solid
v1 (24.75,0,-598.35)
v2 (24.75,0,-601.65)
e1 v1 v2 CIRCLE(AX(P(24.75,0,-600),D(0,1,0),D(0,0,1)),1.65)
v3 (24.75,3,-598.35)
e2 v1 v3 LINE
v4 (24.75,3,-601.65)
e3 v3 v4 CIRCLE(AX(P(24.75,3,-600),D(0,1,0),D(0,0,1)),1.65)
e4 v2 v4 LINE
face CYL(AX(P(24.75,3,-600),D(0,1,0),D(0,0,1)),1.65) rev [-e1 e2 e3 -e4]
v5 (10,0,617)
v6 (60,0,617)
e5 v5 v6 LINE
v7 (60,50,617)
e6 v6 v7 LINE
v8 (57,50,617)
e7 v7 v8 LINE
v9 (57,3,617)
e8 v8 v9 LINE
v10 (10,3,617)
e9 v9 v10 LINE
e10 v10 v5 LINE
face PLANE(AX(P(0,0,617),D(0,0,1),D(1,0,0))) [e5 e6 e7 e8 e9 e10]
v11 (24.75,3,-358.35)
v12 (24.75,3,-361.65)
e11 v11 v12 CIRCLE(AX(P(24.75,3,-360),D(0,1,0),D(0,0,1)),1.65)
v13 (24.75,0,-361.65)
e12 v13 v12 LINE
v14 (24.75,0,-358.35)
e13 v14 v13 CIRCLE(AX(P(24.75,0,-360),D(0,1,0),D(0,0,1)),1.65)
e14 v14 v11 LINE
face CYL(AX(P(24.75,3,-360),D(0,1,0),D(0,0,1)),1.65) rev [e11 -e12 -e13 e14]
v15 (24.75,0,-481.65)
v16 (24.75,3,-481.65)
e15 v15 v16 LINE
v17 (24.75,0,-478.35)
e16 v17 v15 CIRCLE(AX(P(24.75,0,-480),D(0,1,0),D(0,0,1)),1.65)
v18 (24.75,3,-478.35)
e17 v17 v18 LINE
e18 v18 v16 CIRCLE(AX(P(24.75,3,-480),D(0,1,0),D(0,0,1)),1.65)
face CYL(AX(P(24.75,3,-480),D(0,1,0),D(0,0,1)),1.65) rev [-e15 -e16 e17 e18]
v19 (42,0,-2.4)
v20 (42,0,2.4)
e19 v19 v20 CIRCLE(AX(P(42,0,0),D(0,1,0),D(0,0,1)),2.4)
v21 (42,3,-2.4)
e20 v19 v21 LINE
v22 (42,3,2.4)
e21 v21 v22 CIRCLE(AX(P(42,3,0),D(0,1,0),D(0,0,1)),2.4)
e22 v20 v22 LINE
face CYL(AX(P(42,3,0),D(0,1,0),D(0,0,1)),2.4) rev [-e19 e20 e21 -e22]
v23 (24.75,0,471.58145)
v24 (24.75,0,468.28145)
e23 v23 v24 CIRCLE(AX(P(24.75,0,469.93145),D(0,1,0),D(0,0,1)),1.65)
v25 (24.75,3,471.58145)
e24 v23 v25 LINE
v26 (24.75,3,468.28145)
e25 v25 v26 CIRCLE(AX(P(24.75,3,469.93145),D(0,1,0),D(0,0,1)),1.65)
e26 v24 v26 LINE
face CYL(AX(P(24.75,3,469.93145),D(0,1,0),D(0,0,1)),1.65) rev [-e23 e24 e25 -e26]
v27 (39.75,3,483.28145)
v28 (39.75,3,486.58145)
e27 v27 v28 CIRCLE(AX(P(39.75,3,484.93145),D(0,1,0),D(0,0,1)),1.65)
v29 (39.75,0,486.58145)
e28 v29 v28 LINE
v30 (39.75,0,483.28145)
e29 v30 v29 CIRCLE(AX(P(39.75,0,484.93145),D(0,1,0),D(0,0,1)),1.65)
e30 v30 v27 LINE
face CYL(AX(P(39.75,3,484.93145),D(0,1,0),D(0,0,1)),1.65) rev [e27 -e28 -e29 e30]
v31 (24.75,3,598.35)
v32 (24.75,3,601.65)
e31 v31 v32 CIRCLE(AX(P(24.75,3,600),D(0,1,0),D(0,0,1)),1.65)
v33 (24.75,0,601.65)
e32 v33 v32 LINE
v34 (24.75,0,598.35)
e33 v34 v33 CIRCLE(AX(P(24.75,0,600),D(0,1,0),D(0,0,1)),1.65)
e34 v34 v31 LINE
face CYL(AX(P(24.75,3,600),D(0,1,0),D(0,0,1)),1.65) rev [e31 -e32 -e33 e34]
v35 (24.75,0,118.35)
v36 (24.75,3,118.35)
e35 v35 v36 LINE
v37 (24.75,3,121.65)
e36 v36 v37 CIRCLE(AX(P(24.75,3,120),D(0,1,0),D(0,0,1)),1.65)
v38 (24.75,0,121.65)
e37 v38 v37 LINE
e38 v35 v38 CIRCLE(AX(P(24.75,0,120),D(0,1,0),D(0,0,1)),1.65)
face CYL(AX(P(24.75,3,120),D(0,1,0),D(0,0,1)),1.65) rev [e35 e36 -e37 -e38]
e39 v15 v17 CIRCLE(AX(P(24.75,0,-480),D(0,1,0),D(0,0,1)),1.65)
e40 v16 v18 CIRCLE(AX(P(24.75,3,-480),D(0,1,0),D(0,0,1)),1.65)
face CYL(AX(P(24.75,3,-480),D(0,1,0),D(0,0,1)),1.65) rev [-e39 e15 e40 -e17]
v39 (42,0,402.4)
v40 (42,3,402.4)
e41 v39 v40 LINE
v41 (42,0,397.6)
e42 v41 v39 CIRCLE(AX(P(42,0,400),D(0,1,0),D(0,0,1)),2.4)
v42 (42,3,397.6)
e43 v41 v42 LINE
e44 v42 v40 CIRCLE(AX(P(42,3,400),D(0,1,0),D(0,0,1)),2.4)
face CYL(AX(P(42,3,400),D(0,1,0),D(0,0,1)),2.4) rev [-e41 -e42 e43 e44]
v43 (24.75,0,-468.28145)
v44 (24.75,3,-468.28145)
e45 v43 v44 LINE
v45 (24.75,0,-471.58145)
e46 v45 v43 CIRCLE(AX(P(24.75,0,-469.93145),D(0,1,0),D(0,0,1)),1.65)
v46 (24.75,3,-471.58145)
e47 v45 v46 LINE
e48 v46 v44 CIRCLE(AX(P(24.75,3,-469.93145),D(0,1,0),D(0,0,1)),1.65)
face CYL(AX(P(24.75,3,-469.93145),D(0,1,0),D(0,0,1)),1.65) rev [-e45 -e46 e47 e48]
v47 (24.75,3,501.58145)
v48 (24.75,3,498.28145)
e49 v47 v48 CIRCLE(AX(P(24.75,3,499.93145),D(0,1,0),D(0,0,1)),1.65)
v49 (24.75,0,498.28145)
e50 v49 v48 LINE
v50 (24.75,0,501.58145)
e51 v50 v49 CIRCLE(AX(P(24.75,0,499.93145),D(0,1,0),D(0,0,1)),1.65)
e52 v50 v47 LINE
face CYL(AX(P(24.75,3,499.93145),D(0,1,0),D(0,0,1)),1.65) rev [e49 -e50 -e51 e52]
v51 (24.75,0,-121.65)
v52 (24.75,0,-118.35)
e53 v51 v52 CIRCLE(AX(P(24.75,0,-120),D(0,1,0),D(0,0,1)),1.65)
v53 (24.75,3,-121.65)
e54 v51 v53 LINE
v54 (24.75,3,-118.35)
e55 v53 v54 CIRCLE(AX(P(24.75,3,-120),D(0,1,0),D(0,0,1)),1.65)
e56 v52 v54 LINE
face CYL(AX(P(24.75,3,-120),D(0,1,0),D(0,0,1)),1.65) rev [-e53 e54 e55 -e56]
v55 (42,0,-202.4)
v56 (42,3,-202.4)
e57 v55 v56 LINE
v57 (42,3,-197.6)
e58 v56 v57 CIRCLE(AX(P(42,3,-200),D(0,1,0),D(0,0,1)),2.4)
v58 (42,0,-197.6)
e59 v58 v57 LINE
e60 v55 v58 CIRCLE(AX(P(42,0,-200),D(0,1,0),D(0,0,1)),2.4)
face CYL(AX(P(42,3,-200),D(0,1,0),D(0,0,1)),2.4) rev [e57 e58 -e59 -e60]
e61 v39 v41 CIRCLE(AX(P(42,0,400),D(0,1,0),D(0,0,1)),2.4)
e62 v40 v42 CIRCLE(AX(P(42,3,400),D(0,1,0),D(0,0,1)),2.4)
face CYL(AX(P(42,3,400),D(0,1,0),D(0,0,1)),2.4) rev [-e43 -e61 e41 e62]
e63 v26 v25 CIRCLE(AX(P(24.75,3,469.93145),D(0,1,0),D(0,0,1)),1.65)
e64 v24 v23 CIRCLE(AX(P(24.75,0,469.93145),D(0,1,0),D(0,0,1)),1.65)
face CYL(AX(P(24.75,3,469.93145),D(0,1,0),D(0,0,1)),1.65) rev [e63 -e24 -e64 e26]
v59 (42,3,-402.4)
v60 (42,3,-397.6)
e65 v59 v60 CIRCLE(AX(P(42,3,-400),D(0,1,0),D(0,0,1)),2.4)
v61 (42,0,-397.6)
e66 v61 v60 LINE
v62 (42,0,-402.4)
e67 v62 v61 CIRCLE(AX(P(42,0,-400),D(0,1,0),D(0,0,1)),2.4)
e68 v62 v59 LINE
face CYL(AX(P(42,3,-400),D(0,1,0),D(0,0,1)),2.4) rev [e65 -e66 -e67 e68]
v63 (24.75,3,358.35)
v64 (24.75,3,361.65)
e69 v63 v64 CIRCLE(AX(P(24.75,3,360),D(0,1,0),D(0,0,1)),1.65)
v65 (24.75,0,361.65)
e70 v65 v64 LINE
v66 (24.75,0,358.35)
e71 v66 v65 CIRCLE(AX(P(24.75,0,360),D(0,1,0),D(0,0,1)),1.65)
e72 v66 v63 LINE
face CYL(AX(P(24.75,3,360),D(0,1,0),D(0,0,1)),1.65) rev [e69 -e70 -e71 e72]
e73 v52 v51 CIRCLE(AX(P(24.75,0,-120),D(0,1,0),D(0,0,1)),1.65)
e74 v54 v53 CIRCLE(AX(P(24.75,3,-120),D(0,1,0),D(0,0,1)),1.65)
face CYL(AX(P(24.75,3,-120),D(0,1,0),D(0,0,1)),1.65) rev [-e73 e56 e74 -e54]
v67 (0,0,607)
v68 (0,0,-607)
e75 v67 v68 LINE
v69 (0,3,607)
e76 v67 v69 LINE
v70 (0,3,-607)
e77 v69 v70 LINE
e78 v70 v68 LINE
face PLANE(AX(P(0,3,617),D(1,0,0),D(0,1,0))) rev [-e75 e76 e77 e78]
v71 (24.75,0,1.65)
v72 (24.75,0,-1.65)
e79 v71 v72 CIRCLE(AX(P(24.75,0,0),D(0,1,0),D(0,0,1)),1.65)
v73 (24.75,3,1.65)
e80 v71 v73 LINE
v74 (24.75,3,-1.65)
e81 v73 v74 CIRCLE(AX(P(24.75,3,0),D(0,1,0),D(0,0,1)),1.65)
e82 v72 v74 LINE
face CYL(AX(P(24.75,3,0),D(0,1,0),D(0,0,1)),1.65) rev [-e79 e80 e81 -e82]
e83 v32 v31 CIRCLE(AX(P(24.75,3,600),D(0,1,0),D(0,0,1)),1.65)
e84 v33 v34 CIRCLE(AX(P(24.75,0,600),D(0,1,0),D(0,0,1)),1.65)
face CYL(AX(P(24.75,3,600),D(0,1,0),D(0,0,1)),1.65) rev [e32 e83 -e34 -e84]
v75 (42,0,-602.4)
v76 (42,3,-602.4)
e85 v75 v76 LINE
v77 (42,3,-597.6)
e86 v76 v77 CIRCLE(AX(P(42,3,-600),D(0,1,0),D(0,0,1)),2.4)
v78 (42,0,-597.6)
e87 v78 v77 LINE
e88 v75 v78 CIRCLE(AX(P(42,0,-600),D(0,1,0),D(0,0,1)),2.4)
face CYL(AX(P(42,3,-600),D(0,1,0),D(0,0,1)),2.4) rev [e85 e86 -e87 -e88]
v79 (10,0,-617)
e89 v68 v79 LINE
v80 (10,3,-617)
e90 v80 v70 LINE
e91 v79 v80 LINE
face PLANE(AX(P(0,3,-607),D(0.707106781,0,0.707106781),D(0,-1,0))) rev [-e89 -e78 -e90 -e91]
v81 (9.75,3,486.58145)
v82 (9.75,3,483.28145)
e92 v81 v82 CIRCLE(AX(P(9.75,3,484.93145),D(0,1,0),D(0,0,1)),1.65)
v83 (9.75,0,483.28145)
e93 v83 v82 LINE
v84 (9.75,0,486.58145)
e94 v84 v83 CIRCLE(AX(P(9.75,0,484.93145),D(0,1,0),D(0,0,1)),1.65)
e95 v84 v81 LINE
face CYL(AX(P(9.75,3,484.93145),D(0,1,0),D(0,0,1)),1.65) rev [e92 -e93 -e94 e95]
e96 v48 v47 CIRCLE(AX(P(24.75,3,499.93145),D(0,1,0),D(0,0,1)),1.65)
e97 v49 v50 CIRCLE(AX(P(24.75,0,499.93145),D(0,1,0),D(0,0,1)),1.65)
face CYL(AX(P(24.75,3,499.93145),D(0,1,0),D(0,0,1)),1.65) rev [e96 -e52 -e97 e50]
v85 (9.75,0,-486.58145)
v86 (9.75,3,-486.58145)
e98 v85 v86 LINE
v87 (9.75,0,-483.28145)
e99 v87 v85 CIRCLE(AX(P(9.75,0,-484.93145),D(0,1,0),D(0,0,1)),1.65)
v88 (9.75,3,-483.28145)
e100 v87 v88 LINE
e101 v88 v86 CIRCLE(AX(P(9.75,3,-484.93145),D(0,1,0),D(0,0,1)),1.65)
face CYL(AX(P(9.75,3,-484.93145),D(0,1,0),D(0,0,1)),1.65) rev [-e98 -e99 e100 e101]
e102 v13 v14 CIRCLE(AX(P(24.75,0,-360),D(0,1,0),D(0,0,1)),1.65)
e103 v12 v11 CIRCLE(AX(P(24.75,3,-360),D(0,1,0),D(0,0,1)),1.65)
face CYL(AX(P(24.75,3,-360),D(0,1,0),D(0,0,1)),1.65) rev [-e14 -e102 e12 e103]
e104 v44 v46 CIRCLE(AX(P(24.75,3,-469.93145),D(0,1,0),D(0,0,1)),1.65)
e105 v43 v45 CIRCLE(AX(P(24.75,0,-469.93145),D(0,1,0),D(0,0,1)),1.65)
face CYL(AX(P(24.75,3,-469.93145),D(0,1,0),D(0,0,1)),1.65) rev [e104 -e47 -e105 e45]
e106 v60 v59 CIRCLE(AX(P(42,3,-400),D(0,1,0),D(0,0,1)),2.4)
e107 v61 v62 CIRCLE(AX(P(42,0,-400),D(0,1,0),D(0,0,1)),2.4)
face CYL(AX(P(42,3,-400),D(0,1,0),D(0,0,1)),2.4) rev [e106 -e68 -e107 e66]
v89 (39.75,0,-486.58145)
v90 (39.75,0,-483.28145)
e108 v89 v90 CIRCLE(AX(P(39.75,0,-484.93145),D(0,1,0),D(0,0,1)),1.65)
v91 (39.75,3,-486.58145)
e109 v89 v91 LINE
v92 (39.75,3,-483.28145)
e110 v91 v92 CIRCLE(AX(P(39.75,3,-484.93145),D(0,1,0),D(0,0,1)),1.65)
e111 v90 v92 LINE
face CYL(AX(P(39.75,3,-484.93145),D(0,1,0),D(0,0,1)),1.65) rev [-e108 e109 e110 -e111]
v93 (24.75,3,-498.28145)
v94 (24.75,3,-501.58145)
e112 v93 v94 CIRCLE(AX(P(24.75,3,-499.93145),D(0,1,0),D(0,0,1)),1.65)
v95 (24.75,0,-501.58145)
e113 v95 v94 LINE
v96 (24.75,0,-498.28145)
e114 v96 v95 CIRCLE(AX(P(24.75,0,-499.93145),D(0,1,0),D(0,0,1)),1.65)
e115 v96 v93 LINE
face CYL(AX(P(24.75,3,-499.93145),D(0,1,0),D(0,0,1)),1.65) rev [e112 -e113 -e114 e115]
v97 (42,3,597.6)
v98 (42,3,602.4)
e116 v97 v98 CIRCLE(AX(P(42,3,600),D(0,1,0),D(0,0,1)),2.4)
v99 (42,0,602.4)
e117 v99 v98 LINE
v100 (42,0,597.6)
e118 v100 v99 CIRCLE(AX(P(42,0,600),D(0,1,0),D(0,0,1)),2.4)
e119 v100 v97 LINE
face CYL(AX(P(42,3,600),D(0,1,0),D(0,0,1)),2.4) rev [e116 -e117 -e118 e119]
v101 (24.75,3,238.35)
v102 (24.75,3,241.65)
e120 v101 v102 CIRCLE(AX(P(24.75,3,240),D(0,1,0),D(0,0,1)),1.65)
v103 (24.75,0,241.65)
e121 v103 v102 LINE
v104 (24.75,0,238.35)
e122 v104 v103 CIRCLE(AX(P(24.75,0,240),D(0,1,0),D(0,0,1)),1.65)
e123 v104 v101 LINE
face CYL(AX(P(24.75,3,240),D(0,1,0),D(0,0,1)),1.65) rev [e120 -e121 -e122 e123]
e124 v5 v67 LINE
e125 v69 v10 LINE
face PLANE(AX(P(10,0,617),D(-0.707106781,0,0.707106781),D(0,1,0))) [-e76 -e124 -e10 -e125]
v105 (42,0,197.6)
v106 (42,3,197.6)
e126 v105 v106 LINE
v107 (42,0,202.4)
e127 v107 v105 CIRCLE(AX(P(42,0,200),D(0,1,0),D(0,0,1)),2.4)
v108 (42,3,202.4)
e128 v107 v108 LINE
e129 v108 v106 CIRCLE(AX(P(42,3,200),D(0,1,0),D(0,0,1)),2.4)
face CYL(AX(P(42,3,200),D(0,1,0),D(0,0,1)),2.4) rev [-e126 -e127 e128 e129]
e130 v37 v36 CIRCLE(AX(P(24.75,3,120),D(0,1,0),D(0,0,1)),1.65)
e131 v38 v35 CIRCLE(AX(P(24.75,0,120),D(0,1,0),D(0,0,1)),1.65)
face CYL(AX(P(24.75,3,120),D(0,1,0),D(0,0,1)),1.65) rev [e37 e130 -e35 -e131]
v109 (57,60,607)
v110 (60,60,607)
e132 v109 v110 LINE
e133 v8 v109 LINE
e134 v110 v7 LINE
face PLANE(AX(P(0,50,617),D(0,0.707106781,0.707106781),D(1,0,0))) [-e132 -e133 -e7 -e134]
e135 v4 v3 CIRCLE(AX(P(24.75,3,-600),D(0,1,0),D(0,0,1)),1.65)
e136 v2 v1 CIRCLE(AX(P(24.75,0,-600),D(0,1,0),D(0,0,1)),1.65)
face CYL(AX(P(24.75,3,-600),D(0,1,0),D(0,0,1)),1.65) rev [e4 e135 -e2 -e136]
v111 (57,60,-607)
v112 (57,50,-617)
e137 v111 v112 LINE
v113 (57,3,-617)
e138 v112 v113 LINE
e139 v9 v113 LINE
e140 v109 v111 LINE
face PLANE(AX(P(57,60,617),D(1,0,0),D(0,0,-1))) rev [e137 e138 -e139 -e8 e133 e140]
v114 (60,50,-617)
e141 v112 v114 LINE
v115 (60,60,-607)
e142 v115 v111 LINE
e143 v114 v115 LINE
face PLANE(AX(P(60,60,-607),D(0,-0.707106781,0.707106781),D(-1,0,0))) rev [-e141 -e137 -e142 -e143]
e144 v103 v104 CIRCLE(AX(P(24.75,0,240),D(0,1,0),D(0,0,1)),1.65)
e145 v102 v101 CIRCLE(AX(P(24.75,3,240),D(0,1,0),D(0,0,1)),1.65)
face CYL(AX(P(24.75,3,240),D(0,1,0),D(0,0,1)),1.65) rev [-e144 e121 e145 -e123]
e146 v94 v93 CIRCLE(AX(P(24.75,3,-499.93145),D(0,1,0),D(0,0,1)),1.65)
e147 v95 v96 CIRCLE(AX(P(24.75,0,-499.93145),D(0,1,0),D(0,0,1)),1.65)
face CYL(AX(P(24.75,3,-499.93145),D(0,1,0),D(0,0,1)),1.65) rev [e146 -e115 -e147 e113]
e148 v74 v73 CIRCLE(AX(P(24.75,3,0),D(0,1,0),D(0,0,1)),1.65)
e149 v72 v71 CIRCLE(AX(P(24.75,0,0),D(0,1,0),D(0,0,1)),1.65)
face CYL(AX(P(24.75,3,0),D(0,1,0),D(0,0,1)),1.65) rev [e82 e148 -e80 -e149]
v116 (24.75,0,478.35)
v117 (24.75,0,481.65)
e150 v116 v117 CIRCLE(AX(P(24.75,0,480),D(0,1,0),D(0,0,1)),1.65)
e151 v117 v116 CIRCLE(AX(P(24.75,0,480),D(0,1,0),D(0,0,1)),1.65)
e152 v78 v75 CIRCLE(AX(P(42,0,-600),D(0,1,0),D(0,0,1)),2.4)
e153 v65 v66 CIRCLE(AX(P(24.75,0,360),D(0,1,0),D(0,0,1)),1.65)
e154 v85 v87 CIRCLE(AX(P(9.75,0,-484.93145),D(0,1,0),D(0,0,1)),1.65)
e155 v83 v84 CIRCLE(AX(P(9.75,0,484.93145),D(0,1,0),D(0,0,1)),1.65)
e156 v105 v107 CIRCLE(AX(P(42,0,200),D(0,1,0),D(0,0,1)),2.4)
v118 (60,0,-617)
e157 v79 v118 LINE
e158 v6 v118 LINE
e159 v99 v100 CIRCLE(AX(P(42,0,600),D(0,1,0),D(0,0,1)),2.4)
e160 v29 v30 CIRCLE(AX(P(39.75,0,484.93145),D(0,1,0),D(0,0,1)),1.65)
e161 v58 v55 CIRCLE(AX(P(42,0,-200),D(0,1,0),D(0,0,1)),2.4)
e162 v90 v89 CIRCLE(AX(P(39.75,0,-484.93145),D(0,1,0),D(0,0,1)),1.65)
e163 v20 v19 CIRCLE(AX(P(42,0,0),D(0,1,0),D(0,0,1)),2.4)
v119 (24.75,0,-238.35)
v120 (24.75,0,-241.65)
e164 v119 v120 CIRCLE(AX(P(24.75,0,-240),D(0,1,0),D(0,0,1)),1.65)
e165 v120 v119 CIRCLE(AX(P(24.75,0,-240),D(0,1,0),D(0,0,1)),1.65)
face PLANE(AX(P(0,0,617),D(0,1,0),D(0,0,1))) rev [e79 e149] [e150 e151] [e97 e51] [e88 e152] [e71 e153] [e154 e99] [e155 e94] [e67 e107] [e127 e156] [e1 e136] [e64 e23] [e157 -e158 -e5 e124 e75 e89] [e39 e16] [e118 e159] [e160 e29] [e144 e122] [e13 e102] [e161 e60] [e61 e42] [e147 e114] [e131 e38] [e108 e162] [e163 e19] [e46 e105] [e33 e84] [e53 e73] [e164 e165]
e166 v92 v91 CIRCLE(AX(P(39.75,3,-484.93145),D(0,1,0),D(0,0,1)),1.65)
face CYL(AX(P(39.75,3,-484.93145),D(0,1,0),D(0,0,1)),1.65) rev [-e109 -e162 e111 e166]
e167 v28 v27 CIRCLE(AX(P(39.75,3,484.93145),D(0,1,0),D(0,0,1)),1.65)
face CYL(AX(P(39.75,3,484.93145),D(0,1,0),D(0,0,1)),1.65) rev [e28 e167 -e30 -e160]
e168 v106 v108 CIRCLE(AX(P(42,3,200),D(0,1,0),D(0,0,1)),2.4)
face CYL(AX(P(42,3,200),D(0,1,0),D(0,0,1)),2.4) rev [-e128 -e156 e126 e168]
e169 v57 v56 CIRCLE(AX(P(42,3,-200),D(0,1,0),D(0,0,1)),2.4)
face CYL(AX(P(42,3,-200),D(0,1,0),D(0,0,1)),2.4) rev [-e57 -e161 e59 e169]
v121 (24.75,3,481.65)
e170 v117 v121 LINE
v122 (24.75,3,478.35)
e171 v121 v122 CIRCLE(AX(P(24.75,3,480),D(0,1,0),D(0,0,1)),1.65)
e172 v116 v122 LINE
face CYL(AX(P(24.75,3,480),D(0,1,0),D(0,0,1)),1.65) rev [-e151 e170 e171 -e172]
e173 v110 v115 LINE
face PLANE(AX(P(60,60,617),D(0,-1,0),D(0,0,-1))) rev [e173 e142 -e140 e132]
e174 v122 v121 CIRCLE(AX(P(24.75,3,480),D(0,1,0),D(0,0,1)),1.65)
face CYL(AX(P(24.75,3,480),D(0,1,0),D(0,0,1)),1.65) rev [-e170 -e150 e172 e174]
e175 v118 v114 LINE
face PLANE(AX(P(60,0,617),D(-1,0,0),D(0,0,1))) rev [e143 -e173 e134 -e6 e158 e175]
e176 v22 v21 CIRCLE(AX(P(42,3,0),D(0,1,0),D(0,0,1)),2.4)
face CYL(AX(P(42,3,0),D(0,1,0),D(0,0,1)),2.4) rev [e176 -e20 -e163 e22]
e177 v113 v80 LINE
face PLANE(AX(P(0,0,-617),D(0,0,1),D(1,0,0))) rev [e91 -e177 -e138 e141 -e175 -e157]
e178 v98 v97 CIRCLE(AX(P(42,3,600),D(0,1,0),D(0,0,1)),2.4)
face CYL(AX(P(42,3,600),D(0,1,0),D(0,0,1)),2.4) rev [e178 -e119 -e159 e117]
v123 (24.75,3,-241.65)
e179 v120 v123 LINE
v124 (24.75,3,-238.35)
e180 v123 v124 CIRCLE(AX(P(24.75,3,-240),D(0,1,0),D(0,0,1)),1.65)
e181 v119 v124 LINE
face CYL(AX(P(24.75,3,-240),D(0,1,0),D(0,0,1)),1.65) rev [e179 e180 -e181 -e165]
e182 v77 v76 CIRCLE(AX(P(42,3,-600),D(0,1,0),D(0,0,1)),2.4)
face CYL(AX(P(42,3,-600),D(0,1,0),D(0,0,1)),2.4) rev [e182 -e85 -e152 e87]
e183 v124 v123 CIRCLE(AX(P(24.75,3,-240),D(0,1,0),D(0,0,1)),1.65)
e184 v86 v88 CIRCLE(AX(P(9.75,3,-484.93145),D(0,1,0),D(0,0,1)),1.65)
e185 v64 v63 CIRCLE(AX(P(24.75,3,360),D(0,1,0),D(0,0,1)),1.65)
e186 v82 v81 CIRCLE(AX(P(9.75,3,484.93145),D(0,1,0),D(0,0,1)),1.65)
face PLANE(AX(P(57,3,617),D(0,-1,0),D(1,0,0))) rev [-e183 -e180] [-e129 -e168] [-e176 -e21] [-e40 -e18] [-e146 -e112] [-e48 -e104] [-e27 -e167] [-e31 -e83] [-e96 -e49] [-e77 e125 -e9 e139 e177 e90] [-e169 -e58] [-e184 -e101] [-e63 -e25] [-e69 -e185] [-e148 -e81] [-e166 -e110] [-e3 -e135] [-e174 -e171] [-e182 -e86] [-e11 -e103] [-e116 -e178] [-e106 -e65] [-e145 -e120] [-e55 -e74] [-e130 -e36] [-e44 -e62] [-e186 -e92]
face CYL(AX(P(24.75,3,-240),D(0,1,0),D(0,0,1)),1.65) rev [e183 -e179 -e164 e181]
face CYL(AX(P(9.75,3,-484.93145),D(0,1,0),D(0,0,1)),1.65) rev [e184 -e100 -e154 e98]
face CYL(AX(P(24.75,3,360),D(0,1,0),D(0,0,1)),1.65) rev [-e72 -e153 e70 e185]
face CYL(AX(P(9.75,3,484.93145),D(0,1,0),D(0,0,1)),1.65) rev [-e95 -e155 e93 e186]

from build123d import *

# Parameters (mm, degrees)
EXTRUDE_1_DEPTH        = 617
HOLE_WIZARD_M4_2_D     = 3.3
HOLE_WIZARD_M4_3_D     = 3.3
HOLE_WIZARD_M4_3_DEPTH = 3
HOLE_WIZARD_M4_1_D     = 4.8
HOLE_WIZARD_M4_4_D     = 3.3
CHAMFER_1_SIZE         = 10


with BuildPart() as part:
    # 草图1 → 凸台-拉伸1 (new, symmetric)
    with BuildSketch(Plane.XY):
        Polygon((0, 0), (60, 0), (60, 60), (57, 60), (57, 3), (0, 3), align=None)
    extrude(amount=EXTRUDE_1_DEPTH, both=True)

    # M4 螺纹孔2 (through all)
    with Locations(Plane(origin=(0, 3, 0), x_dir=(1, 0, 0), z_dir=(0, 1, 0))):
        with Locations((24.75, 499.931449769), (9.75, 484.931449769), (39.75, 484.931449769), (39.75, -484.931449769), (9.75, -484.931449769), (24.75, -499.931449769)):
            Hole(HOLE_WIZARD_M4_2_D / 2)

    # M4 螺纹孔3
    with Locations(Plane(origin=(0, 3, 0), x_dir=(1, 0, 0), z_dir=(0, 1, 0))):
        with Locations((9.75, 484.931449769), (39.75, 484.931449769), (24.75, 469.931449769), (24.75, 499.931449769), (24.75, -499.931449769), (24.75, -469.931449769), (39.75, -484.931449769), (9.75, -484.931449769)):
            Hole(HOLE_WIZARD_M4_3_D / 2, depth=HOLE_WIZARD_M4_3_DEPTH)

    # M4 间隙孔1 (through all)
    with Locations(Plane(origin=(0, 3, 0), x_dir=(1, 0, 0), z_dir=(0, 1, 0))):
        with Locations((42, 0), (42, 200), (42, 400), (42, 600), (42, -600), (42, -400), (42, -200)):
            Hole(HOLE_WIZARD_M4_1_D / 2)

    # M4 螺纹孔4 (through all)
    with Locations(Plane(origin=(0, 3, 0), x_dir=(1, 0, 0), z_dir=(0, 1, 0))):
        with Locations((24.75, 0), (24.75, 120), (24.75, 240), (24.75, 360), (24.75, 480), (24.75, 600), (24.75, -600), (24.75, -480), (24.75, -360), (24.75, -240), (24.75, -120)):
            Hole(HOLE_WIZARD_M4_4_D / 2)

    # 倒角1
    chamfer_1_edges = [part.edges().sort_by_distance(p)[0] for p in [
        (58.5, 60, 617),
        (0, 1.5, 617),
        (58.5, 60, -617),
        (0, 1.5, -617),
    ]]
    chamfer(chamfer_1_edges, length=CHAMFER_1_SIZE)


solid = part.part
